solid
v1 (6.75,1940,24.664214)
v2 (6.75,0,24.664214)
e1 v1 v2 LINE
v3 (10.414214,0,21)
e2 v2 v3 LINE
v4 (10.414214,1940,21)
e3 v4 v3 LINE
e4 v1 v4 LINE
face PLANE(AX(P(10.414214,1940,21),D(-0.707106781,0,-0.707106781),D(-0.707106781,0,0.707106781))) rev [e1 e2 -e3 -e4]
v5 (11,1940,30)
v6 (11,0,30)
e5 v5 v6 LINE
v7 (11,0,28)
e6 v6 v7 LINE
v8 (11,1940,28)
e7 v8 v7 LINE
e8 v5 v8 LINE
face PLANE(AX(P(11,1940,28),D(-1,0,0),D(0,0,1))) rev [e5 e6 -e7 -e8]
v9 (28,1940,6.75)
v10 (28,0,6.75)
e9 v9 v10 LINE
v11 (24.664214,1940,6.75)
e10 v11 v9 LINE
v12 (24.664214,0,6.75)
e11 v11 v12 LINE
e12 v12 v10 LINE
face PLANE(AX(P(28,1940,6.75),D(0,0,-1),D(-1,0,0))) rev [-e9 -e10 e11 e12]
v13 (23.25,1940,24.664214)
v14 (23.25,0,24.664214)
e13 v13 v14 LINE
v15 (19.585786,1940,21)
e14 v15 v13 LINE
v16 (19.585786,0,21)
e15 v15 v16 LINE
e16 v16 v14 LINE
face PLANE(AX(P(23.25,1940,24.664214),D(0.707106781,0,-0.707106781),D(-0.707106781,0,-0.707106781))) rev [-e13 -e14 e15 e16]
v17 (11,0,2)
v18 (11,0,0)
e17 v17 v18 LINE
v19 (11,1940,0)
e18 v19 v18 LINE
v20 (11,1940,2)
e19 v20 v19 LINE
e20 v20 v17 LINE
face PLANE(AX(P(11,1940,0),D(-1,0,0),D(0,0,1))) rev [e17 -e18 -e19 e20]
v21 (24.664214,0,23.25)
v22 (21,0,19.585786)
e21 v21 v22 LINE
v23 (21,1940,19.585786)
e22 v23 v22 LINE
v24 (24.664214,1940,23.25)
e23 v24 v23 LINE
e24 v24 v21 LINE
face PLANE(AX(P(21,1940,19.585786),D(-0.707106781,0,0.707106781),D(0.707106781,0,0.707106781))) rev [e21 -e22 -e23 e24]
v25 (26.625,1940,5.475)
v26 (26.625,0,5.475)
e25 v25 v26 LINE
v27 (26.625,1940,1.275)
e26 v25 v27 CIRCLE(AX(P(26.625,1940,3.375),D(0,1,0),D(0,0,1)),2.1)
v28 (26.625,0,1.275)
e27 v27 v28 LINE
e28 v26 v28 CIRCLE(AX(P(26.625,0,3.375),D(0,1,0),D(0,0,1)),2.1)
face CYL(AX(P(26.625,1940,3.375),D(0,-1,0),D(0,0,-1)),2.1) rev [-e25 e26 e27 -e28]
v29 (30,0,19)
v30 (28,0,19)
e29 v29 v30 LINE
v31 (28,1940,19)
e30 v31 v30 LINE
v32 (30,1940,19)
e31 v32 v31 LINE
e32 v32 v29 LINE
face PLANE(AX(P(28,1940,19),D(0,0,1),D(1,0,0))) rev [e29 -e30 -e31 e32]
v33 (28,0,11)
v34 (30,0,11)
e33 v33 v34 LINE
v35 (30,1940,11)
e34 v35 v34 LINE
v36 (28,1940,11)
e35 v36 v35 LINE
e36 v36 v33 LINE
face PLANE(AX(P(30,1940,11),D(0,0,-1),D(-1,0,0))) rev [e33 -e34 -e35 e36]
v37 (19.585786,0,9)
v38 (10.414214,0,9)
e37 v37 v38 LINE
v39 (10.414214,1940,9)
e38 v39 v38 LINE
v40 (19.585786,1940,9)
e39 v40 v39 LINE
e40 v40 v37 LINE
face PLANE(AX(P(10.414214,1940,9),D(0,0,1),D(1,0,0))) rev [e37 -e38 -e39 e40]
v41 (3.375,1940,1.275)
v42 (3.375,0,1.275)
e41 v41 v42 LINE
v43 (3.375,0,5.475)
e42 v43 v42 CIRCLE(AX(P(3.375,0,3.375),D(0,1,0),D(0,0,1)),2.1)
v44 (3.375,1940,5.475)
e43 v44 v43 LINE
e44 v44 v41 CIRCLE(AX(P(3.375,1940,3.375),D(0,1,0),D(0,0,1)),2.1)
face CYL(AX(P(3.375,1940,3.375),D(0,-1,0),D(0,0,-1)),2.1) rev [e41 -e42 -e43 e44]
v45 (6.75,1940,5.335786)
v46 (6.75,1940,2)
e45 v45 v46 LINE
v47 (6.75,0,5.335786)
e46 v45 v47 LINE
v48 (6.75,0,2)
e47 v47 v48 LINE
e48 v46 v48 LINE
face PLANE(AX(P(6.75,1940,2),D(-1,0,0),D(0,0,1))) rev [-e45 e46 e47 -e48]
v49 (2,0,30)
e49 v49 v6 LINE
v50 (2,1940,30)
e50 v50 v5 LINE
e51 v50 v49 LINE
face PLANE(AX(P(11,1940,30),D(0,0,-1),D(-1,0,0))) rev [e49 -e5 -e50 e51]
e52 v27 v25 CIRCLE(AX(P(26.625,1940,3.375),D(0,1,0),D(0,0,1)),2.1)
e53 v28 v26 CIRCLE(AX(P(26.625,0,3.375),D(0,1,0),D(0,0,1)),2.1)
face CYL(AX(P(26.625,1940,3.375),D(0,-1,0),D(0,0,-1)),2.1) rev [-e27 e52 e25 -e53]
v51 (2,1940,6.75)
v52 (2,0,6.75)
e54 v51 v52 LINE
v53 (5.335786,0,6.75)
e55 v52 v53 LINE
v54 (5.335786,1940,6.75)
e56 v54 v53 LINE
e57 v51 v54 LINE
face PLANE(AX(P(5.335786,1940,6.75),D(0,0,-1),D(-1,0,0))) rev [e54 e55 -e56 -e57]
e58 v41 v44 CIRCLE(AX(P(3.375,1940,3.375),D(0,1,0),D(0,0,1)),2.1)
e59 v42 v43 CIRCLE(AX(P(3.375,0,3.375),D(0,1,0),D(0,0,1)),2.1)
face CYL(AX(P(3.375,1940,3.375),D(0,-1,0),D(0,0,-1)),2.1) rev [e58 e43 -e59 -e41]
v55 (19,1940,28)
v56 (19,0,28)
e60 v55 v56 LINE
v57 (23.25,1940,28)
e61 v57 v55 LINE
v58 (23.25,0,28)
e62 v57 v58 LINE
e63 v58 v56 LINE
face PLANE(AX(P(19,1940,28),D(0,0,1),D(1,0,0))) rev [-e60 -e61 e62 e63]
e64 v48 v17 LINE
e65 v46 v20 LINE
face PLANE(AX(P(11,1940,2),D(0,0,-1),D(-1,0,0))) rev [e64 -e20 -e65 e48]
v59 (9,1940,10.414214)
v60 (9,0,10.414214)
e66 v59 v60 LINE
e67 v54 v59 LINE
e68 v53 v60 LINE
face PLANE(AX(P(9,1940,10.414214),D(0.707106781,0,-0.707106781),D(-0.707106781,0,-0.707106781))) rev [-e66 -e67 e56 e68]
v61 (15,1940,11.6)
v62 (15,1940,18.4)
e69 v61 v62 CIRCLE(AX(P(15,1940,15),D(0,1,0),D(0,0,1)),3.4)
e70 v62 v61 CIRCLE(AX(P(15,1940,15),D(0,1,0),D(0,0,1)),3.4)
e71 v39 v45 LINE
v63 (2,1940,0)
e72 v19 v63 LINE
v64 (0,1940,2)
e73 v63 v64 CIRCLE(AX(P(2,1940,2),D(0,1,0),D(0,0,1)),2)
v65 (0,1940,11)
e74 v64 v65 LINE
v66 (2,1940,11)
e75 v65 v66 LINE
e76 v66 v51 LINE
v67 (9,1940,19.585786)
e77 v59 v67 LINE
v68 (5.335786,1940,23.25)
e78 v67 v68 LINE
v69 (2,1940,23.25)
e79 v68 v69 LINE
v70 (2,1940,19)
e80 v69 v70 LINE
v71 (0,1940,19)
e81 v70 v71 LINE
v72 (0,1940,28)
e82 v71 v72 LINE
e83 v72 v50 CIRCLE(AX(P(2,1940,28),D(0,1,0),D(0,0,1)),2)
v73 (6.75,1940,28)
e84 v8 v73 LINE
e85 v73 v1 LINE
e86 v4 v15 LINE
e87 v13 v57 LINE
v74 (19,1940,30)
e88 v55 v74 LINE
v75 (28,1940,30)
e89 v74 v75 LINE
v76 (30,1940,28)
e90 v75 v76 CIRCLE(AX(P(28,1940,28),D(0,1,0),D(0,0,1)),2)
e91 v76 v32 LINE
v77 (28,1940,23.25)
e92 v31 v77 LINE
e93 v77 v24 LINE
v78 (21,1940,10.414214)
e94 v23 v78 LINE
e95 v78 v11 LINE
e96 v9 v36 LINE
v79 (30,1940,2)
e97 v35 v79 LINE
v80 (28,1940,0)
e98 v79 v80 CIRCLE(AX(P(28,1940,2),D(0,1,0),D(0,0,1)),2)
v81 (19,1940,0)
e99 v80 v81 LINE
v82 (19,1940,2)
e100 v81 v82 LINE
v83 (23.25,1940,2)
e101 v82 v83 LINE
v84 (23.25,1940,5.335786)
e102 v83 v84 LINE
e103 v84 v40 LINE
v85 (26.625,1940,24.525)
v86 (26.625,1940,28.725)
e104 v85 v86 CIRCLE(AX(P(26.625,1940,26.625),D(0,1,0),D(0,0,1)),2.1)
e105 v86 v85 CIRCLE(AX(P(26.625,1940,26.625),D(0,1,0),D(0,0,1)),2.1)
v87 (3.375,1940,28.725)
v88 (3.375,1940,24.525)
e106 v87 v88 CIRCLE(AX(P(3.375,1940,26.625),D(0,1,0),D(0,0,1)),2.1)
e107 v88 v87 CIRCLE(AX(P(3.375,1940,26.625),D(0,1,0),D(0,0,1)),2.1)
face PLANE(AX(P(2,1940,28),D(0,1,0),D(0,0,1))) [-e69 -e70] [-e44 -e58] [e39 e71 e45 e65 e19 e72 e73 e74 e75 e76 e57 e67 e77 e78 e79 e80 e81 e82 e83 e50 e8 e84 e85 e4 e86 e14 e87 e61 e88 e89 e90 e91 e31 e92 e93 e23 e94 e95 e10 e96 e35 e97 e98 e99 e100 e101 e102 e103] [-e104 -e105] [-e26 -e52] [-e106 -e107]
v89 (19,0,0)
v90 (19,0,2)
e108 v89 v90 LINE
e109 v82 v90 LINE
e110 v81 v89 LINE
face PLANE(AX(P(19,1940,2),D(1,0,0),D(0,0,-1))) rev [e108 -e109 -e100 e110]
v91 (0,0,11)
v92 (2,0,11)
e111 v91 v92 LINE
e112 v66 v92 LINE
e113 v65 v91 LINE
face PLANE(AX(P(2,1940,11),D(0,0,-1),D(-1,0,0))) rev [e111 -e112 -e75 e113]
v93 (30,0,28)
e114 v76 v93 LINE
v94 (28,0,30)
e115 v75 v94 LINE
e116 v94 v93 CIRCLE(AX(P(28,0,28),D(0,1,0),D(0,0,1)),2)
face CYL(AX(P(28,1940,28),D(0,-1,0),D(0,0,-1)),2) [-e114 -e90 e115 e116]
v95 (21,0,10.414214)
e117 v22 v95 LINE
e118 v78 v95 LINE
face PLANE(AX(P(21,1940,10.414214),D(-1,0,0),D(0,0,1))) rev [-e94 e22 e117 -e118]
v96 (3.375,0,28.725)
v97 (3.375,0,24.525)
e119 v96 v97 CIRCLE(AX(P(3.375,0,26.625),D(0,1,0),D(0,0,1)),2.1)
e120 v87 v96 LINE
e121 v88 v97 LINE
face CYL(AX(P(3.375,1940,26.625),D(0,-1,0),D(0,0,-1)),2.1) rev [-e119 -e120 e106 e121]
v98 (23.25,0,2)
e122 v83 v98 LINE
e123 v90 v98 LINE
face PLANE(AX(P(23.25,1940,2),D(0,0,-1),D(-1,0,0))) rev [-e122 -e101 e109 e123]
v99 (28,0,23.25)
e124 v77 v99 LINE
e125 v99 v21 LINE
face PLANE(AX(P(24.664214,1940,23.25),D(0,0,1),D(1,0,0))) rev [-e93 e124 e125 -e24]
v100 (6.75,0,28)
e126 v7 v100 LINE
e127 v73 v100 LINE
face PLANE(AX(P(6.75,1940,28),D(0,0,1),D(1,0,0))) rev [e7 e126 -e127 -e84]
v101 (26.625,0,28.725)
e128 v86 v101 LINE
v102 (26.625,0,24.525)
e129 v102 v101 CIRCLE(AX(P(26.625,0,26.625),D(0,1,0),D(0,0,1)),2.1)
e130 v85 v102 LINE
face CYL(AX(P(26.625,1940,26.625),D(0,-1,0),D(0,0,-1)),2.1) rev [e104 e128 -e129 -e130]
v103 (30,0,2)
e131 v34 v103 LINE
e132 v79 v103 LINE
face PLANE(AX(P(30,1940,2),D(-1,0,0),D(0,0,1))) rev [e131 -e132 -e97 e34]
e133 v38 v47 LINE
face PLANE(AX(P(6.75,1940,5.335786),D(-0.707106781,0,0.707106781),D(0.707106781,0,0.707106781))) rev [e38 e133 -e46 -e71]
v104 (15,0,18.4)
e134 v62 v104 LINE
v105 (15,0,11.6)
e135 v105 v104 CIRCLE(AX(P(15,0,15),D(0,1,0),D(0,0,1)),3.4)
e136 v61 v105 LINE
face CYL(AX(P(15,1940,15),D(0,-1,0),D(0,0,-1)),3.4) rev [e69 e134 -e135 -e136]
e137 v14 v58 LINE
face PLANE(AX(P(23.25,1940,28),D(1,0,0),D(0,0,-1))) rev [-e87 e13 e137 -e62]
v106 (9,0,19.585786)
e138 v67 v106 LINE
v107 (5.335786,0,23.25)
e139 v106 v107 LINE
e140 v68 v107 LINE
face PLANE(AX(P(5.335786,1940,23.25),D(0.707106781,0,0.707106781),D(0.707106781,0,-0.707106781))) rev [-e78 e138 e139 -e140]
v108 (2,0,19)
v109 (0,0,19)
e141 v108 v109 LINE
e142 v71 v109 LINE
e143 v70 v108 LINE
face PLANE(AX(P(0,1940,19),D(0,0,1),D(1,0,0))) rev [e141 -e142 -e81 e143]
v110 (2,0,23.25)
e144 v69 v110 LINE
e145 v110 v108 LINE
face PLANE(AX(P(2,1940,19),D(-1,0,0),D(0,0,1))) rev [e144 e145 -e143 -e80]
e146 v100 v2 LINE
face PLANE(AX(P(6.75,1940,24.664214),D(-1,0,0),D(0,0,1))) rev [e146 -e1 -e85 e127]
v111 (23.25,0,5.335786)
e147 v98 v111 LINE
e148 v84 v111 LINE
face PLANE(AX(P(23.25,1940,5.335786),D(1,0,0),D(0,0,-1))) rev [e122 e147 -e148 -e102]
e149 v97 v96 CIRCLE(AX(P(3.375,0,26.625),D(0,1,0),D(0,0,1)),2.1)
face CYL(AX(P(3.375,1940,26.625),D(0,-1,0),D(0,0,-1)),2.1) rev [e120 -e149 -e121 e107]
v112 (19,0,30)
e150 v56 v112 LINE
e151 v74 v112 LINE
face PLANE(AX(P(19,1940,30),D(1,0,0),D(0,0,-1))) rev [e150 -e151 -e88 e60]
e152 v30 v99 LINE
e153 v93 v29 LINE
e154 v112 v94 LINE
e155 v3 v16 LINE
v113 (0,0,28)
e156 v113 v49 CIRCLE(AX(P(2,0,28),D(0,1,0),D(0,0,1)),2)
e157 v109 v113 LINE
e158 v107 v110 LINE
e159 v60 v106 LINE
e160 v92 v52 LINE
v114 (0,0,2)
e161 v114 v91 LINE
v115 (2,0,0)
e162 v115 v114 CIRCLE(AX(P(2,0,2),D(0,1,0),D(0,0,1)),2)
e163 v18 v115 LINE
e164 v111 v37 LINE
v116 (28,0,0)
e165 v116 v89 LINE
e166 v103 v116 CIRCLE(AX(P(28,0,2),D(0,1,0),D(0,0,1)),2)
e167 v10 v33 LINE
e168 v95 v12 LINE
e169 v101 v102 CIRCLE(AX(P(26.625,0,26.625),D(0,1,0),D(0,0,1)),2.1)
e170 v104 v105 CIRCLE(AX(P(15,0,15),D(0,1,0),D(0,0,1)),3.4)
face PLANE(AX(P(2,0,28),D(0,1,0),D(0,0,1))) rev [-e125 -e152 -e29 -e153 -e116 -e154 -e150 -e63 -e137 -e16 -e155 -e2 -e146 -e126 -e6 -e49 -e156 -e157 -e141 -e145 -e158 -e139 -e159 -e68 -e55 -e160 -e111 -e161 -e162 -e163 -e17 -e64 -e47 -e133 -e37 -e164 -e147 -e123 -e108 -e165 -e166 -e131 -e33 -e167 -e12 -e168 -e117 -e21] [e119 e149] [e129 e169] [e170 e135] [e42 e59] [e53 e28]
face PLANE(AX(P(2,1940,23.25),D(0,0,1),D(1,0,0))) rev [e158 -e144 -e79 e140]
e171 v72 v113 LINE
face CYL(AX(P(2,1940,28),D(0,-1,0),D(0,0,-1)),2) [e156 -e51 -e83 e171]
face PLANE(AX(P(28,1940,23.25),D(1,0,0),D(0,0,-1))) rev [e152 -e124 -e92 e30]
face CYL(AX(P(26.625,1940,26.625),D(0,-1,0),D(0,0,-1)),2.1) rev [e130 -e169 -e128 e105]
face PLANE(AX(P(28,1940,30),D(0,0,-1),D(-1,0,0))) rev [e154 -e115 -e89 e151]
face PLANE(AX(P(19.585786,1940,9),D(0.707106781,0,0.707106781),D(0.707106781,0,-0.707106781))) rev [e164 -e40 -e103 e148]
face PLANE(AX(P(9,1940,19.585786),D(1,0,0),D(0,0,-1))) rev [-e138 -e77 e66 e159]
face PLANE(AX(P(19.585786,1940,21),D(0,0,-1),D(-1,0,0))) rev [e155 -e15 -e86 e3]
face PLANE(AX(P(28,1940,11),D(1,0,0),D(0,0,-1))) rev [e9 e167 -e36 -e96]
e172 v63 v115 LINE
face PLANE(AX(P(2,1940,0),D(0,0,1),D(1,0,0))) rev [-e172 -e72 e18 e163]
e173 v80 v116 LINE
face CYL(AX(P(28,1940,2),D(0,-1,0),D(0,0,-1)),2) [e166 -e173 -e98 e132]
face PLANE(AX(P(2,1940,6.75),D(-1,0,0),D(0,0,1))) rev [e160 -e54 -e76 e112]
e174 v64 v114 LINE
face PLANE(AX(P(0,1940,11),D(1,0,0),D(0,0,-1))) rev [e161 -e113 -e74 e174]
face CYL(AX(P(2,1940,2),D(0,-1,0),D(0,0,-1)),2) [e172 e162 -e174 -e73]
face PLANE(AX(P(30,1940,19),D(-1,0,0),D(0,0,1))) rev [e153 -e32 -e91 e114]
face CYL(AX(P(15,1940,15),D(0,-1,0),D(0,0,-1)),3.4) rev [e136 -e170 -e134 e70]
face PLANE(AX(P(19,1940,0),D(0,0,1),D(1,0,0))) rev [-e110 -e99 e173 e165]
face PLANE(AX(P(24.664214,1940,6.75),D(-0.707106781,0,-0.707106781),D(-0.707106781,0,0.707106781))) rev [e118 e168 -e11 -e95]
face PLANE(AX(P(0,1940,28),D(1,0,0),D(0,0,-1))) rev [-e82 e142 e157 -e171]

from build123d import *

# Parameters (mm, degrees)
SKETCH_1_R      = 2.1
SKETCH_1_R_2    = 3.4
EXTRUDE_1_DEPTH = 1940


with BuildPart() as part:
    # 草图1 → 拉伸1 (new body)
    with BuildSketch(Plane(origin=(0, 0, 0), x_dir=(1, 0, 0), z_dir=(0, 1, 0))):
        with BuildLine():
            Line((6.75, -28), (11, -28))
            Line((11, -28), (11, -30))
            Line((11, -30), (2, -30))
            ThreePointArc((2, -30), (0.585786438, -29.414213562), (0, -28))
            Line((0, -28), (0, -19))
            Line((0, -19), (2, -19))
            Line((2, -19), (2, -23.25))
            Line((2, -23.25), (5.335785999, -23.25))
            Line((5.335785999, -23.25), (9, -19.585785999))
            Line((9, -19.585785999), (9, -10.414214001))
            Line((9, -10.414214001), (5.335785999, -6.75))
            Line((5.335785999, -6.75), (2, -6.75))
            Line((2, -6.75), (2, -11))
            Line((2, -11), (0, -11))
            Line((0, -11), (0, -2))
            ThreePointArc((0, -2), (0.585786438, -0.585786438), (2, 0))
            Line((2, 0), (11, 0))
            Line((11, 0), (11, -2))
            Line((11, -2), (6.75, -2))
            Line((6.75, -2), (6.75, -5.335785999))
            Line((6.75, -5.335785999), (10.414214001, -9))
            Line((10.414214001, -9), (19.585785999, -9))
            Line((19.585785999, -9), (23.25, -5.335785999))
            Line((23.25, -5.335785999), (23.25, -2))
            Line((23.25, -2), (19, -2))
            Line((19, -2), (19, 0))
            Line((19, 0), (28, 0))
            ThreePointArc((28, 0), (29.414213562, -0.585786438), (30, -2))
            Line((30, -2), (30, -11))
            Line((30, -11), (28, -11))
            Line((28, -11), (28, -6.75))
            Line((28, -6.75), (24.664214001, -6.75))
            Line((24.664214001, -6.75), (21, -10.414214001))
            Line((21, -10.414214001), (21, -19.585785999))
            Line((21, -19.585785999), (24.664214001, -23.25))
            Line((24.664214001, -23.25), (28, -23.25))
            Line((28, -23.25), (28, -19))
            Line((28, -19), (30, -19))
            Line((30, -19), (30, -28))
            ThreePointArc((30, -28), (29.414213562, -29.414213562), (28, -30))
            Line((28, -30), (19, -30))
            Line((19, -30), (19, -28))
            Line((19, -28), (23.25, -28))
            Line((23.25, -28), (23.25, -24.664214001))
            Line((23.25, -24.664214001), (19.585785999, -21))
            Line((19.585785999, -21), (10.414214001, -21))
            Line((10.414214001, -21), (6.75, -24.664214001))
            Line((6.75, -24.664214001), (6.75, -28))
        make_face()
        with Locations(Location((3.375, -26.625, 0), (0, 0, 270))):
            Circle(SKETCH_1_R, mode=Mode.SUBTRACT)
        with Locations(Location((26.625, -26.625, 0), (0, 0, 270))):
            Circle(SKETCH_1_R, mode=Mode.SUBTRACT)
        with Locations(Location((15, -15, 0), (0, 0, 270))):
            Circle(SKETCH_1_R_2, mode=Mode.SUBTRACT)
        with Locations(Location((3.375, -3.375, 0), (0, 0, 270))):
            Circle(SKETCH_1_R, mode=Mode.SUBTRACT)
        with Locations(Location((26.625, -3.375, 0), (0, 0, 270))):
            Circle(SKETCH_1_R, mode=Mode.SUBTRACT)
    extrude(amount=EXTRUDE_1_DEPTH)


solid = part.part
